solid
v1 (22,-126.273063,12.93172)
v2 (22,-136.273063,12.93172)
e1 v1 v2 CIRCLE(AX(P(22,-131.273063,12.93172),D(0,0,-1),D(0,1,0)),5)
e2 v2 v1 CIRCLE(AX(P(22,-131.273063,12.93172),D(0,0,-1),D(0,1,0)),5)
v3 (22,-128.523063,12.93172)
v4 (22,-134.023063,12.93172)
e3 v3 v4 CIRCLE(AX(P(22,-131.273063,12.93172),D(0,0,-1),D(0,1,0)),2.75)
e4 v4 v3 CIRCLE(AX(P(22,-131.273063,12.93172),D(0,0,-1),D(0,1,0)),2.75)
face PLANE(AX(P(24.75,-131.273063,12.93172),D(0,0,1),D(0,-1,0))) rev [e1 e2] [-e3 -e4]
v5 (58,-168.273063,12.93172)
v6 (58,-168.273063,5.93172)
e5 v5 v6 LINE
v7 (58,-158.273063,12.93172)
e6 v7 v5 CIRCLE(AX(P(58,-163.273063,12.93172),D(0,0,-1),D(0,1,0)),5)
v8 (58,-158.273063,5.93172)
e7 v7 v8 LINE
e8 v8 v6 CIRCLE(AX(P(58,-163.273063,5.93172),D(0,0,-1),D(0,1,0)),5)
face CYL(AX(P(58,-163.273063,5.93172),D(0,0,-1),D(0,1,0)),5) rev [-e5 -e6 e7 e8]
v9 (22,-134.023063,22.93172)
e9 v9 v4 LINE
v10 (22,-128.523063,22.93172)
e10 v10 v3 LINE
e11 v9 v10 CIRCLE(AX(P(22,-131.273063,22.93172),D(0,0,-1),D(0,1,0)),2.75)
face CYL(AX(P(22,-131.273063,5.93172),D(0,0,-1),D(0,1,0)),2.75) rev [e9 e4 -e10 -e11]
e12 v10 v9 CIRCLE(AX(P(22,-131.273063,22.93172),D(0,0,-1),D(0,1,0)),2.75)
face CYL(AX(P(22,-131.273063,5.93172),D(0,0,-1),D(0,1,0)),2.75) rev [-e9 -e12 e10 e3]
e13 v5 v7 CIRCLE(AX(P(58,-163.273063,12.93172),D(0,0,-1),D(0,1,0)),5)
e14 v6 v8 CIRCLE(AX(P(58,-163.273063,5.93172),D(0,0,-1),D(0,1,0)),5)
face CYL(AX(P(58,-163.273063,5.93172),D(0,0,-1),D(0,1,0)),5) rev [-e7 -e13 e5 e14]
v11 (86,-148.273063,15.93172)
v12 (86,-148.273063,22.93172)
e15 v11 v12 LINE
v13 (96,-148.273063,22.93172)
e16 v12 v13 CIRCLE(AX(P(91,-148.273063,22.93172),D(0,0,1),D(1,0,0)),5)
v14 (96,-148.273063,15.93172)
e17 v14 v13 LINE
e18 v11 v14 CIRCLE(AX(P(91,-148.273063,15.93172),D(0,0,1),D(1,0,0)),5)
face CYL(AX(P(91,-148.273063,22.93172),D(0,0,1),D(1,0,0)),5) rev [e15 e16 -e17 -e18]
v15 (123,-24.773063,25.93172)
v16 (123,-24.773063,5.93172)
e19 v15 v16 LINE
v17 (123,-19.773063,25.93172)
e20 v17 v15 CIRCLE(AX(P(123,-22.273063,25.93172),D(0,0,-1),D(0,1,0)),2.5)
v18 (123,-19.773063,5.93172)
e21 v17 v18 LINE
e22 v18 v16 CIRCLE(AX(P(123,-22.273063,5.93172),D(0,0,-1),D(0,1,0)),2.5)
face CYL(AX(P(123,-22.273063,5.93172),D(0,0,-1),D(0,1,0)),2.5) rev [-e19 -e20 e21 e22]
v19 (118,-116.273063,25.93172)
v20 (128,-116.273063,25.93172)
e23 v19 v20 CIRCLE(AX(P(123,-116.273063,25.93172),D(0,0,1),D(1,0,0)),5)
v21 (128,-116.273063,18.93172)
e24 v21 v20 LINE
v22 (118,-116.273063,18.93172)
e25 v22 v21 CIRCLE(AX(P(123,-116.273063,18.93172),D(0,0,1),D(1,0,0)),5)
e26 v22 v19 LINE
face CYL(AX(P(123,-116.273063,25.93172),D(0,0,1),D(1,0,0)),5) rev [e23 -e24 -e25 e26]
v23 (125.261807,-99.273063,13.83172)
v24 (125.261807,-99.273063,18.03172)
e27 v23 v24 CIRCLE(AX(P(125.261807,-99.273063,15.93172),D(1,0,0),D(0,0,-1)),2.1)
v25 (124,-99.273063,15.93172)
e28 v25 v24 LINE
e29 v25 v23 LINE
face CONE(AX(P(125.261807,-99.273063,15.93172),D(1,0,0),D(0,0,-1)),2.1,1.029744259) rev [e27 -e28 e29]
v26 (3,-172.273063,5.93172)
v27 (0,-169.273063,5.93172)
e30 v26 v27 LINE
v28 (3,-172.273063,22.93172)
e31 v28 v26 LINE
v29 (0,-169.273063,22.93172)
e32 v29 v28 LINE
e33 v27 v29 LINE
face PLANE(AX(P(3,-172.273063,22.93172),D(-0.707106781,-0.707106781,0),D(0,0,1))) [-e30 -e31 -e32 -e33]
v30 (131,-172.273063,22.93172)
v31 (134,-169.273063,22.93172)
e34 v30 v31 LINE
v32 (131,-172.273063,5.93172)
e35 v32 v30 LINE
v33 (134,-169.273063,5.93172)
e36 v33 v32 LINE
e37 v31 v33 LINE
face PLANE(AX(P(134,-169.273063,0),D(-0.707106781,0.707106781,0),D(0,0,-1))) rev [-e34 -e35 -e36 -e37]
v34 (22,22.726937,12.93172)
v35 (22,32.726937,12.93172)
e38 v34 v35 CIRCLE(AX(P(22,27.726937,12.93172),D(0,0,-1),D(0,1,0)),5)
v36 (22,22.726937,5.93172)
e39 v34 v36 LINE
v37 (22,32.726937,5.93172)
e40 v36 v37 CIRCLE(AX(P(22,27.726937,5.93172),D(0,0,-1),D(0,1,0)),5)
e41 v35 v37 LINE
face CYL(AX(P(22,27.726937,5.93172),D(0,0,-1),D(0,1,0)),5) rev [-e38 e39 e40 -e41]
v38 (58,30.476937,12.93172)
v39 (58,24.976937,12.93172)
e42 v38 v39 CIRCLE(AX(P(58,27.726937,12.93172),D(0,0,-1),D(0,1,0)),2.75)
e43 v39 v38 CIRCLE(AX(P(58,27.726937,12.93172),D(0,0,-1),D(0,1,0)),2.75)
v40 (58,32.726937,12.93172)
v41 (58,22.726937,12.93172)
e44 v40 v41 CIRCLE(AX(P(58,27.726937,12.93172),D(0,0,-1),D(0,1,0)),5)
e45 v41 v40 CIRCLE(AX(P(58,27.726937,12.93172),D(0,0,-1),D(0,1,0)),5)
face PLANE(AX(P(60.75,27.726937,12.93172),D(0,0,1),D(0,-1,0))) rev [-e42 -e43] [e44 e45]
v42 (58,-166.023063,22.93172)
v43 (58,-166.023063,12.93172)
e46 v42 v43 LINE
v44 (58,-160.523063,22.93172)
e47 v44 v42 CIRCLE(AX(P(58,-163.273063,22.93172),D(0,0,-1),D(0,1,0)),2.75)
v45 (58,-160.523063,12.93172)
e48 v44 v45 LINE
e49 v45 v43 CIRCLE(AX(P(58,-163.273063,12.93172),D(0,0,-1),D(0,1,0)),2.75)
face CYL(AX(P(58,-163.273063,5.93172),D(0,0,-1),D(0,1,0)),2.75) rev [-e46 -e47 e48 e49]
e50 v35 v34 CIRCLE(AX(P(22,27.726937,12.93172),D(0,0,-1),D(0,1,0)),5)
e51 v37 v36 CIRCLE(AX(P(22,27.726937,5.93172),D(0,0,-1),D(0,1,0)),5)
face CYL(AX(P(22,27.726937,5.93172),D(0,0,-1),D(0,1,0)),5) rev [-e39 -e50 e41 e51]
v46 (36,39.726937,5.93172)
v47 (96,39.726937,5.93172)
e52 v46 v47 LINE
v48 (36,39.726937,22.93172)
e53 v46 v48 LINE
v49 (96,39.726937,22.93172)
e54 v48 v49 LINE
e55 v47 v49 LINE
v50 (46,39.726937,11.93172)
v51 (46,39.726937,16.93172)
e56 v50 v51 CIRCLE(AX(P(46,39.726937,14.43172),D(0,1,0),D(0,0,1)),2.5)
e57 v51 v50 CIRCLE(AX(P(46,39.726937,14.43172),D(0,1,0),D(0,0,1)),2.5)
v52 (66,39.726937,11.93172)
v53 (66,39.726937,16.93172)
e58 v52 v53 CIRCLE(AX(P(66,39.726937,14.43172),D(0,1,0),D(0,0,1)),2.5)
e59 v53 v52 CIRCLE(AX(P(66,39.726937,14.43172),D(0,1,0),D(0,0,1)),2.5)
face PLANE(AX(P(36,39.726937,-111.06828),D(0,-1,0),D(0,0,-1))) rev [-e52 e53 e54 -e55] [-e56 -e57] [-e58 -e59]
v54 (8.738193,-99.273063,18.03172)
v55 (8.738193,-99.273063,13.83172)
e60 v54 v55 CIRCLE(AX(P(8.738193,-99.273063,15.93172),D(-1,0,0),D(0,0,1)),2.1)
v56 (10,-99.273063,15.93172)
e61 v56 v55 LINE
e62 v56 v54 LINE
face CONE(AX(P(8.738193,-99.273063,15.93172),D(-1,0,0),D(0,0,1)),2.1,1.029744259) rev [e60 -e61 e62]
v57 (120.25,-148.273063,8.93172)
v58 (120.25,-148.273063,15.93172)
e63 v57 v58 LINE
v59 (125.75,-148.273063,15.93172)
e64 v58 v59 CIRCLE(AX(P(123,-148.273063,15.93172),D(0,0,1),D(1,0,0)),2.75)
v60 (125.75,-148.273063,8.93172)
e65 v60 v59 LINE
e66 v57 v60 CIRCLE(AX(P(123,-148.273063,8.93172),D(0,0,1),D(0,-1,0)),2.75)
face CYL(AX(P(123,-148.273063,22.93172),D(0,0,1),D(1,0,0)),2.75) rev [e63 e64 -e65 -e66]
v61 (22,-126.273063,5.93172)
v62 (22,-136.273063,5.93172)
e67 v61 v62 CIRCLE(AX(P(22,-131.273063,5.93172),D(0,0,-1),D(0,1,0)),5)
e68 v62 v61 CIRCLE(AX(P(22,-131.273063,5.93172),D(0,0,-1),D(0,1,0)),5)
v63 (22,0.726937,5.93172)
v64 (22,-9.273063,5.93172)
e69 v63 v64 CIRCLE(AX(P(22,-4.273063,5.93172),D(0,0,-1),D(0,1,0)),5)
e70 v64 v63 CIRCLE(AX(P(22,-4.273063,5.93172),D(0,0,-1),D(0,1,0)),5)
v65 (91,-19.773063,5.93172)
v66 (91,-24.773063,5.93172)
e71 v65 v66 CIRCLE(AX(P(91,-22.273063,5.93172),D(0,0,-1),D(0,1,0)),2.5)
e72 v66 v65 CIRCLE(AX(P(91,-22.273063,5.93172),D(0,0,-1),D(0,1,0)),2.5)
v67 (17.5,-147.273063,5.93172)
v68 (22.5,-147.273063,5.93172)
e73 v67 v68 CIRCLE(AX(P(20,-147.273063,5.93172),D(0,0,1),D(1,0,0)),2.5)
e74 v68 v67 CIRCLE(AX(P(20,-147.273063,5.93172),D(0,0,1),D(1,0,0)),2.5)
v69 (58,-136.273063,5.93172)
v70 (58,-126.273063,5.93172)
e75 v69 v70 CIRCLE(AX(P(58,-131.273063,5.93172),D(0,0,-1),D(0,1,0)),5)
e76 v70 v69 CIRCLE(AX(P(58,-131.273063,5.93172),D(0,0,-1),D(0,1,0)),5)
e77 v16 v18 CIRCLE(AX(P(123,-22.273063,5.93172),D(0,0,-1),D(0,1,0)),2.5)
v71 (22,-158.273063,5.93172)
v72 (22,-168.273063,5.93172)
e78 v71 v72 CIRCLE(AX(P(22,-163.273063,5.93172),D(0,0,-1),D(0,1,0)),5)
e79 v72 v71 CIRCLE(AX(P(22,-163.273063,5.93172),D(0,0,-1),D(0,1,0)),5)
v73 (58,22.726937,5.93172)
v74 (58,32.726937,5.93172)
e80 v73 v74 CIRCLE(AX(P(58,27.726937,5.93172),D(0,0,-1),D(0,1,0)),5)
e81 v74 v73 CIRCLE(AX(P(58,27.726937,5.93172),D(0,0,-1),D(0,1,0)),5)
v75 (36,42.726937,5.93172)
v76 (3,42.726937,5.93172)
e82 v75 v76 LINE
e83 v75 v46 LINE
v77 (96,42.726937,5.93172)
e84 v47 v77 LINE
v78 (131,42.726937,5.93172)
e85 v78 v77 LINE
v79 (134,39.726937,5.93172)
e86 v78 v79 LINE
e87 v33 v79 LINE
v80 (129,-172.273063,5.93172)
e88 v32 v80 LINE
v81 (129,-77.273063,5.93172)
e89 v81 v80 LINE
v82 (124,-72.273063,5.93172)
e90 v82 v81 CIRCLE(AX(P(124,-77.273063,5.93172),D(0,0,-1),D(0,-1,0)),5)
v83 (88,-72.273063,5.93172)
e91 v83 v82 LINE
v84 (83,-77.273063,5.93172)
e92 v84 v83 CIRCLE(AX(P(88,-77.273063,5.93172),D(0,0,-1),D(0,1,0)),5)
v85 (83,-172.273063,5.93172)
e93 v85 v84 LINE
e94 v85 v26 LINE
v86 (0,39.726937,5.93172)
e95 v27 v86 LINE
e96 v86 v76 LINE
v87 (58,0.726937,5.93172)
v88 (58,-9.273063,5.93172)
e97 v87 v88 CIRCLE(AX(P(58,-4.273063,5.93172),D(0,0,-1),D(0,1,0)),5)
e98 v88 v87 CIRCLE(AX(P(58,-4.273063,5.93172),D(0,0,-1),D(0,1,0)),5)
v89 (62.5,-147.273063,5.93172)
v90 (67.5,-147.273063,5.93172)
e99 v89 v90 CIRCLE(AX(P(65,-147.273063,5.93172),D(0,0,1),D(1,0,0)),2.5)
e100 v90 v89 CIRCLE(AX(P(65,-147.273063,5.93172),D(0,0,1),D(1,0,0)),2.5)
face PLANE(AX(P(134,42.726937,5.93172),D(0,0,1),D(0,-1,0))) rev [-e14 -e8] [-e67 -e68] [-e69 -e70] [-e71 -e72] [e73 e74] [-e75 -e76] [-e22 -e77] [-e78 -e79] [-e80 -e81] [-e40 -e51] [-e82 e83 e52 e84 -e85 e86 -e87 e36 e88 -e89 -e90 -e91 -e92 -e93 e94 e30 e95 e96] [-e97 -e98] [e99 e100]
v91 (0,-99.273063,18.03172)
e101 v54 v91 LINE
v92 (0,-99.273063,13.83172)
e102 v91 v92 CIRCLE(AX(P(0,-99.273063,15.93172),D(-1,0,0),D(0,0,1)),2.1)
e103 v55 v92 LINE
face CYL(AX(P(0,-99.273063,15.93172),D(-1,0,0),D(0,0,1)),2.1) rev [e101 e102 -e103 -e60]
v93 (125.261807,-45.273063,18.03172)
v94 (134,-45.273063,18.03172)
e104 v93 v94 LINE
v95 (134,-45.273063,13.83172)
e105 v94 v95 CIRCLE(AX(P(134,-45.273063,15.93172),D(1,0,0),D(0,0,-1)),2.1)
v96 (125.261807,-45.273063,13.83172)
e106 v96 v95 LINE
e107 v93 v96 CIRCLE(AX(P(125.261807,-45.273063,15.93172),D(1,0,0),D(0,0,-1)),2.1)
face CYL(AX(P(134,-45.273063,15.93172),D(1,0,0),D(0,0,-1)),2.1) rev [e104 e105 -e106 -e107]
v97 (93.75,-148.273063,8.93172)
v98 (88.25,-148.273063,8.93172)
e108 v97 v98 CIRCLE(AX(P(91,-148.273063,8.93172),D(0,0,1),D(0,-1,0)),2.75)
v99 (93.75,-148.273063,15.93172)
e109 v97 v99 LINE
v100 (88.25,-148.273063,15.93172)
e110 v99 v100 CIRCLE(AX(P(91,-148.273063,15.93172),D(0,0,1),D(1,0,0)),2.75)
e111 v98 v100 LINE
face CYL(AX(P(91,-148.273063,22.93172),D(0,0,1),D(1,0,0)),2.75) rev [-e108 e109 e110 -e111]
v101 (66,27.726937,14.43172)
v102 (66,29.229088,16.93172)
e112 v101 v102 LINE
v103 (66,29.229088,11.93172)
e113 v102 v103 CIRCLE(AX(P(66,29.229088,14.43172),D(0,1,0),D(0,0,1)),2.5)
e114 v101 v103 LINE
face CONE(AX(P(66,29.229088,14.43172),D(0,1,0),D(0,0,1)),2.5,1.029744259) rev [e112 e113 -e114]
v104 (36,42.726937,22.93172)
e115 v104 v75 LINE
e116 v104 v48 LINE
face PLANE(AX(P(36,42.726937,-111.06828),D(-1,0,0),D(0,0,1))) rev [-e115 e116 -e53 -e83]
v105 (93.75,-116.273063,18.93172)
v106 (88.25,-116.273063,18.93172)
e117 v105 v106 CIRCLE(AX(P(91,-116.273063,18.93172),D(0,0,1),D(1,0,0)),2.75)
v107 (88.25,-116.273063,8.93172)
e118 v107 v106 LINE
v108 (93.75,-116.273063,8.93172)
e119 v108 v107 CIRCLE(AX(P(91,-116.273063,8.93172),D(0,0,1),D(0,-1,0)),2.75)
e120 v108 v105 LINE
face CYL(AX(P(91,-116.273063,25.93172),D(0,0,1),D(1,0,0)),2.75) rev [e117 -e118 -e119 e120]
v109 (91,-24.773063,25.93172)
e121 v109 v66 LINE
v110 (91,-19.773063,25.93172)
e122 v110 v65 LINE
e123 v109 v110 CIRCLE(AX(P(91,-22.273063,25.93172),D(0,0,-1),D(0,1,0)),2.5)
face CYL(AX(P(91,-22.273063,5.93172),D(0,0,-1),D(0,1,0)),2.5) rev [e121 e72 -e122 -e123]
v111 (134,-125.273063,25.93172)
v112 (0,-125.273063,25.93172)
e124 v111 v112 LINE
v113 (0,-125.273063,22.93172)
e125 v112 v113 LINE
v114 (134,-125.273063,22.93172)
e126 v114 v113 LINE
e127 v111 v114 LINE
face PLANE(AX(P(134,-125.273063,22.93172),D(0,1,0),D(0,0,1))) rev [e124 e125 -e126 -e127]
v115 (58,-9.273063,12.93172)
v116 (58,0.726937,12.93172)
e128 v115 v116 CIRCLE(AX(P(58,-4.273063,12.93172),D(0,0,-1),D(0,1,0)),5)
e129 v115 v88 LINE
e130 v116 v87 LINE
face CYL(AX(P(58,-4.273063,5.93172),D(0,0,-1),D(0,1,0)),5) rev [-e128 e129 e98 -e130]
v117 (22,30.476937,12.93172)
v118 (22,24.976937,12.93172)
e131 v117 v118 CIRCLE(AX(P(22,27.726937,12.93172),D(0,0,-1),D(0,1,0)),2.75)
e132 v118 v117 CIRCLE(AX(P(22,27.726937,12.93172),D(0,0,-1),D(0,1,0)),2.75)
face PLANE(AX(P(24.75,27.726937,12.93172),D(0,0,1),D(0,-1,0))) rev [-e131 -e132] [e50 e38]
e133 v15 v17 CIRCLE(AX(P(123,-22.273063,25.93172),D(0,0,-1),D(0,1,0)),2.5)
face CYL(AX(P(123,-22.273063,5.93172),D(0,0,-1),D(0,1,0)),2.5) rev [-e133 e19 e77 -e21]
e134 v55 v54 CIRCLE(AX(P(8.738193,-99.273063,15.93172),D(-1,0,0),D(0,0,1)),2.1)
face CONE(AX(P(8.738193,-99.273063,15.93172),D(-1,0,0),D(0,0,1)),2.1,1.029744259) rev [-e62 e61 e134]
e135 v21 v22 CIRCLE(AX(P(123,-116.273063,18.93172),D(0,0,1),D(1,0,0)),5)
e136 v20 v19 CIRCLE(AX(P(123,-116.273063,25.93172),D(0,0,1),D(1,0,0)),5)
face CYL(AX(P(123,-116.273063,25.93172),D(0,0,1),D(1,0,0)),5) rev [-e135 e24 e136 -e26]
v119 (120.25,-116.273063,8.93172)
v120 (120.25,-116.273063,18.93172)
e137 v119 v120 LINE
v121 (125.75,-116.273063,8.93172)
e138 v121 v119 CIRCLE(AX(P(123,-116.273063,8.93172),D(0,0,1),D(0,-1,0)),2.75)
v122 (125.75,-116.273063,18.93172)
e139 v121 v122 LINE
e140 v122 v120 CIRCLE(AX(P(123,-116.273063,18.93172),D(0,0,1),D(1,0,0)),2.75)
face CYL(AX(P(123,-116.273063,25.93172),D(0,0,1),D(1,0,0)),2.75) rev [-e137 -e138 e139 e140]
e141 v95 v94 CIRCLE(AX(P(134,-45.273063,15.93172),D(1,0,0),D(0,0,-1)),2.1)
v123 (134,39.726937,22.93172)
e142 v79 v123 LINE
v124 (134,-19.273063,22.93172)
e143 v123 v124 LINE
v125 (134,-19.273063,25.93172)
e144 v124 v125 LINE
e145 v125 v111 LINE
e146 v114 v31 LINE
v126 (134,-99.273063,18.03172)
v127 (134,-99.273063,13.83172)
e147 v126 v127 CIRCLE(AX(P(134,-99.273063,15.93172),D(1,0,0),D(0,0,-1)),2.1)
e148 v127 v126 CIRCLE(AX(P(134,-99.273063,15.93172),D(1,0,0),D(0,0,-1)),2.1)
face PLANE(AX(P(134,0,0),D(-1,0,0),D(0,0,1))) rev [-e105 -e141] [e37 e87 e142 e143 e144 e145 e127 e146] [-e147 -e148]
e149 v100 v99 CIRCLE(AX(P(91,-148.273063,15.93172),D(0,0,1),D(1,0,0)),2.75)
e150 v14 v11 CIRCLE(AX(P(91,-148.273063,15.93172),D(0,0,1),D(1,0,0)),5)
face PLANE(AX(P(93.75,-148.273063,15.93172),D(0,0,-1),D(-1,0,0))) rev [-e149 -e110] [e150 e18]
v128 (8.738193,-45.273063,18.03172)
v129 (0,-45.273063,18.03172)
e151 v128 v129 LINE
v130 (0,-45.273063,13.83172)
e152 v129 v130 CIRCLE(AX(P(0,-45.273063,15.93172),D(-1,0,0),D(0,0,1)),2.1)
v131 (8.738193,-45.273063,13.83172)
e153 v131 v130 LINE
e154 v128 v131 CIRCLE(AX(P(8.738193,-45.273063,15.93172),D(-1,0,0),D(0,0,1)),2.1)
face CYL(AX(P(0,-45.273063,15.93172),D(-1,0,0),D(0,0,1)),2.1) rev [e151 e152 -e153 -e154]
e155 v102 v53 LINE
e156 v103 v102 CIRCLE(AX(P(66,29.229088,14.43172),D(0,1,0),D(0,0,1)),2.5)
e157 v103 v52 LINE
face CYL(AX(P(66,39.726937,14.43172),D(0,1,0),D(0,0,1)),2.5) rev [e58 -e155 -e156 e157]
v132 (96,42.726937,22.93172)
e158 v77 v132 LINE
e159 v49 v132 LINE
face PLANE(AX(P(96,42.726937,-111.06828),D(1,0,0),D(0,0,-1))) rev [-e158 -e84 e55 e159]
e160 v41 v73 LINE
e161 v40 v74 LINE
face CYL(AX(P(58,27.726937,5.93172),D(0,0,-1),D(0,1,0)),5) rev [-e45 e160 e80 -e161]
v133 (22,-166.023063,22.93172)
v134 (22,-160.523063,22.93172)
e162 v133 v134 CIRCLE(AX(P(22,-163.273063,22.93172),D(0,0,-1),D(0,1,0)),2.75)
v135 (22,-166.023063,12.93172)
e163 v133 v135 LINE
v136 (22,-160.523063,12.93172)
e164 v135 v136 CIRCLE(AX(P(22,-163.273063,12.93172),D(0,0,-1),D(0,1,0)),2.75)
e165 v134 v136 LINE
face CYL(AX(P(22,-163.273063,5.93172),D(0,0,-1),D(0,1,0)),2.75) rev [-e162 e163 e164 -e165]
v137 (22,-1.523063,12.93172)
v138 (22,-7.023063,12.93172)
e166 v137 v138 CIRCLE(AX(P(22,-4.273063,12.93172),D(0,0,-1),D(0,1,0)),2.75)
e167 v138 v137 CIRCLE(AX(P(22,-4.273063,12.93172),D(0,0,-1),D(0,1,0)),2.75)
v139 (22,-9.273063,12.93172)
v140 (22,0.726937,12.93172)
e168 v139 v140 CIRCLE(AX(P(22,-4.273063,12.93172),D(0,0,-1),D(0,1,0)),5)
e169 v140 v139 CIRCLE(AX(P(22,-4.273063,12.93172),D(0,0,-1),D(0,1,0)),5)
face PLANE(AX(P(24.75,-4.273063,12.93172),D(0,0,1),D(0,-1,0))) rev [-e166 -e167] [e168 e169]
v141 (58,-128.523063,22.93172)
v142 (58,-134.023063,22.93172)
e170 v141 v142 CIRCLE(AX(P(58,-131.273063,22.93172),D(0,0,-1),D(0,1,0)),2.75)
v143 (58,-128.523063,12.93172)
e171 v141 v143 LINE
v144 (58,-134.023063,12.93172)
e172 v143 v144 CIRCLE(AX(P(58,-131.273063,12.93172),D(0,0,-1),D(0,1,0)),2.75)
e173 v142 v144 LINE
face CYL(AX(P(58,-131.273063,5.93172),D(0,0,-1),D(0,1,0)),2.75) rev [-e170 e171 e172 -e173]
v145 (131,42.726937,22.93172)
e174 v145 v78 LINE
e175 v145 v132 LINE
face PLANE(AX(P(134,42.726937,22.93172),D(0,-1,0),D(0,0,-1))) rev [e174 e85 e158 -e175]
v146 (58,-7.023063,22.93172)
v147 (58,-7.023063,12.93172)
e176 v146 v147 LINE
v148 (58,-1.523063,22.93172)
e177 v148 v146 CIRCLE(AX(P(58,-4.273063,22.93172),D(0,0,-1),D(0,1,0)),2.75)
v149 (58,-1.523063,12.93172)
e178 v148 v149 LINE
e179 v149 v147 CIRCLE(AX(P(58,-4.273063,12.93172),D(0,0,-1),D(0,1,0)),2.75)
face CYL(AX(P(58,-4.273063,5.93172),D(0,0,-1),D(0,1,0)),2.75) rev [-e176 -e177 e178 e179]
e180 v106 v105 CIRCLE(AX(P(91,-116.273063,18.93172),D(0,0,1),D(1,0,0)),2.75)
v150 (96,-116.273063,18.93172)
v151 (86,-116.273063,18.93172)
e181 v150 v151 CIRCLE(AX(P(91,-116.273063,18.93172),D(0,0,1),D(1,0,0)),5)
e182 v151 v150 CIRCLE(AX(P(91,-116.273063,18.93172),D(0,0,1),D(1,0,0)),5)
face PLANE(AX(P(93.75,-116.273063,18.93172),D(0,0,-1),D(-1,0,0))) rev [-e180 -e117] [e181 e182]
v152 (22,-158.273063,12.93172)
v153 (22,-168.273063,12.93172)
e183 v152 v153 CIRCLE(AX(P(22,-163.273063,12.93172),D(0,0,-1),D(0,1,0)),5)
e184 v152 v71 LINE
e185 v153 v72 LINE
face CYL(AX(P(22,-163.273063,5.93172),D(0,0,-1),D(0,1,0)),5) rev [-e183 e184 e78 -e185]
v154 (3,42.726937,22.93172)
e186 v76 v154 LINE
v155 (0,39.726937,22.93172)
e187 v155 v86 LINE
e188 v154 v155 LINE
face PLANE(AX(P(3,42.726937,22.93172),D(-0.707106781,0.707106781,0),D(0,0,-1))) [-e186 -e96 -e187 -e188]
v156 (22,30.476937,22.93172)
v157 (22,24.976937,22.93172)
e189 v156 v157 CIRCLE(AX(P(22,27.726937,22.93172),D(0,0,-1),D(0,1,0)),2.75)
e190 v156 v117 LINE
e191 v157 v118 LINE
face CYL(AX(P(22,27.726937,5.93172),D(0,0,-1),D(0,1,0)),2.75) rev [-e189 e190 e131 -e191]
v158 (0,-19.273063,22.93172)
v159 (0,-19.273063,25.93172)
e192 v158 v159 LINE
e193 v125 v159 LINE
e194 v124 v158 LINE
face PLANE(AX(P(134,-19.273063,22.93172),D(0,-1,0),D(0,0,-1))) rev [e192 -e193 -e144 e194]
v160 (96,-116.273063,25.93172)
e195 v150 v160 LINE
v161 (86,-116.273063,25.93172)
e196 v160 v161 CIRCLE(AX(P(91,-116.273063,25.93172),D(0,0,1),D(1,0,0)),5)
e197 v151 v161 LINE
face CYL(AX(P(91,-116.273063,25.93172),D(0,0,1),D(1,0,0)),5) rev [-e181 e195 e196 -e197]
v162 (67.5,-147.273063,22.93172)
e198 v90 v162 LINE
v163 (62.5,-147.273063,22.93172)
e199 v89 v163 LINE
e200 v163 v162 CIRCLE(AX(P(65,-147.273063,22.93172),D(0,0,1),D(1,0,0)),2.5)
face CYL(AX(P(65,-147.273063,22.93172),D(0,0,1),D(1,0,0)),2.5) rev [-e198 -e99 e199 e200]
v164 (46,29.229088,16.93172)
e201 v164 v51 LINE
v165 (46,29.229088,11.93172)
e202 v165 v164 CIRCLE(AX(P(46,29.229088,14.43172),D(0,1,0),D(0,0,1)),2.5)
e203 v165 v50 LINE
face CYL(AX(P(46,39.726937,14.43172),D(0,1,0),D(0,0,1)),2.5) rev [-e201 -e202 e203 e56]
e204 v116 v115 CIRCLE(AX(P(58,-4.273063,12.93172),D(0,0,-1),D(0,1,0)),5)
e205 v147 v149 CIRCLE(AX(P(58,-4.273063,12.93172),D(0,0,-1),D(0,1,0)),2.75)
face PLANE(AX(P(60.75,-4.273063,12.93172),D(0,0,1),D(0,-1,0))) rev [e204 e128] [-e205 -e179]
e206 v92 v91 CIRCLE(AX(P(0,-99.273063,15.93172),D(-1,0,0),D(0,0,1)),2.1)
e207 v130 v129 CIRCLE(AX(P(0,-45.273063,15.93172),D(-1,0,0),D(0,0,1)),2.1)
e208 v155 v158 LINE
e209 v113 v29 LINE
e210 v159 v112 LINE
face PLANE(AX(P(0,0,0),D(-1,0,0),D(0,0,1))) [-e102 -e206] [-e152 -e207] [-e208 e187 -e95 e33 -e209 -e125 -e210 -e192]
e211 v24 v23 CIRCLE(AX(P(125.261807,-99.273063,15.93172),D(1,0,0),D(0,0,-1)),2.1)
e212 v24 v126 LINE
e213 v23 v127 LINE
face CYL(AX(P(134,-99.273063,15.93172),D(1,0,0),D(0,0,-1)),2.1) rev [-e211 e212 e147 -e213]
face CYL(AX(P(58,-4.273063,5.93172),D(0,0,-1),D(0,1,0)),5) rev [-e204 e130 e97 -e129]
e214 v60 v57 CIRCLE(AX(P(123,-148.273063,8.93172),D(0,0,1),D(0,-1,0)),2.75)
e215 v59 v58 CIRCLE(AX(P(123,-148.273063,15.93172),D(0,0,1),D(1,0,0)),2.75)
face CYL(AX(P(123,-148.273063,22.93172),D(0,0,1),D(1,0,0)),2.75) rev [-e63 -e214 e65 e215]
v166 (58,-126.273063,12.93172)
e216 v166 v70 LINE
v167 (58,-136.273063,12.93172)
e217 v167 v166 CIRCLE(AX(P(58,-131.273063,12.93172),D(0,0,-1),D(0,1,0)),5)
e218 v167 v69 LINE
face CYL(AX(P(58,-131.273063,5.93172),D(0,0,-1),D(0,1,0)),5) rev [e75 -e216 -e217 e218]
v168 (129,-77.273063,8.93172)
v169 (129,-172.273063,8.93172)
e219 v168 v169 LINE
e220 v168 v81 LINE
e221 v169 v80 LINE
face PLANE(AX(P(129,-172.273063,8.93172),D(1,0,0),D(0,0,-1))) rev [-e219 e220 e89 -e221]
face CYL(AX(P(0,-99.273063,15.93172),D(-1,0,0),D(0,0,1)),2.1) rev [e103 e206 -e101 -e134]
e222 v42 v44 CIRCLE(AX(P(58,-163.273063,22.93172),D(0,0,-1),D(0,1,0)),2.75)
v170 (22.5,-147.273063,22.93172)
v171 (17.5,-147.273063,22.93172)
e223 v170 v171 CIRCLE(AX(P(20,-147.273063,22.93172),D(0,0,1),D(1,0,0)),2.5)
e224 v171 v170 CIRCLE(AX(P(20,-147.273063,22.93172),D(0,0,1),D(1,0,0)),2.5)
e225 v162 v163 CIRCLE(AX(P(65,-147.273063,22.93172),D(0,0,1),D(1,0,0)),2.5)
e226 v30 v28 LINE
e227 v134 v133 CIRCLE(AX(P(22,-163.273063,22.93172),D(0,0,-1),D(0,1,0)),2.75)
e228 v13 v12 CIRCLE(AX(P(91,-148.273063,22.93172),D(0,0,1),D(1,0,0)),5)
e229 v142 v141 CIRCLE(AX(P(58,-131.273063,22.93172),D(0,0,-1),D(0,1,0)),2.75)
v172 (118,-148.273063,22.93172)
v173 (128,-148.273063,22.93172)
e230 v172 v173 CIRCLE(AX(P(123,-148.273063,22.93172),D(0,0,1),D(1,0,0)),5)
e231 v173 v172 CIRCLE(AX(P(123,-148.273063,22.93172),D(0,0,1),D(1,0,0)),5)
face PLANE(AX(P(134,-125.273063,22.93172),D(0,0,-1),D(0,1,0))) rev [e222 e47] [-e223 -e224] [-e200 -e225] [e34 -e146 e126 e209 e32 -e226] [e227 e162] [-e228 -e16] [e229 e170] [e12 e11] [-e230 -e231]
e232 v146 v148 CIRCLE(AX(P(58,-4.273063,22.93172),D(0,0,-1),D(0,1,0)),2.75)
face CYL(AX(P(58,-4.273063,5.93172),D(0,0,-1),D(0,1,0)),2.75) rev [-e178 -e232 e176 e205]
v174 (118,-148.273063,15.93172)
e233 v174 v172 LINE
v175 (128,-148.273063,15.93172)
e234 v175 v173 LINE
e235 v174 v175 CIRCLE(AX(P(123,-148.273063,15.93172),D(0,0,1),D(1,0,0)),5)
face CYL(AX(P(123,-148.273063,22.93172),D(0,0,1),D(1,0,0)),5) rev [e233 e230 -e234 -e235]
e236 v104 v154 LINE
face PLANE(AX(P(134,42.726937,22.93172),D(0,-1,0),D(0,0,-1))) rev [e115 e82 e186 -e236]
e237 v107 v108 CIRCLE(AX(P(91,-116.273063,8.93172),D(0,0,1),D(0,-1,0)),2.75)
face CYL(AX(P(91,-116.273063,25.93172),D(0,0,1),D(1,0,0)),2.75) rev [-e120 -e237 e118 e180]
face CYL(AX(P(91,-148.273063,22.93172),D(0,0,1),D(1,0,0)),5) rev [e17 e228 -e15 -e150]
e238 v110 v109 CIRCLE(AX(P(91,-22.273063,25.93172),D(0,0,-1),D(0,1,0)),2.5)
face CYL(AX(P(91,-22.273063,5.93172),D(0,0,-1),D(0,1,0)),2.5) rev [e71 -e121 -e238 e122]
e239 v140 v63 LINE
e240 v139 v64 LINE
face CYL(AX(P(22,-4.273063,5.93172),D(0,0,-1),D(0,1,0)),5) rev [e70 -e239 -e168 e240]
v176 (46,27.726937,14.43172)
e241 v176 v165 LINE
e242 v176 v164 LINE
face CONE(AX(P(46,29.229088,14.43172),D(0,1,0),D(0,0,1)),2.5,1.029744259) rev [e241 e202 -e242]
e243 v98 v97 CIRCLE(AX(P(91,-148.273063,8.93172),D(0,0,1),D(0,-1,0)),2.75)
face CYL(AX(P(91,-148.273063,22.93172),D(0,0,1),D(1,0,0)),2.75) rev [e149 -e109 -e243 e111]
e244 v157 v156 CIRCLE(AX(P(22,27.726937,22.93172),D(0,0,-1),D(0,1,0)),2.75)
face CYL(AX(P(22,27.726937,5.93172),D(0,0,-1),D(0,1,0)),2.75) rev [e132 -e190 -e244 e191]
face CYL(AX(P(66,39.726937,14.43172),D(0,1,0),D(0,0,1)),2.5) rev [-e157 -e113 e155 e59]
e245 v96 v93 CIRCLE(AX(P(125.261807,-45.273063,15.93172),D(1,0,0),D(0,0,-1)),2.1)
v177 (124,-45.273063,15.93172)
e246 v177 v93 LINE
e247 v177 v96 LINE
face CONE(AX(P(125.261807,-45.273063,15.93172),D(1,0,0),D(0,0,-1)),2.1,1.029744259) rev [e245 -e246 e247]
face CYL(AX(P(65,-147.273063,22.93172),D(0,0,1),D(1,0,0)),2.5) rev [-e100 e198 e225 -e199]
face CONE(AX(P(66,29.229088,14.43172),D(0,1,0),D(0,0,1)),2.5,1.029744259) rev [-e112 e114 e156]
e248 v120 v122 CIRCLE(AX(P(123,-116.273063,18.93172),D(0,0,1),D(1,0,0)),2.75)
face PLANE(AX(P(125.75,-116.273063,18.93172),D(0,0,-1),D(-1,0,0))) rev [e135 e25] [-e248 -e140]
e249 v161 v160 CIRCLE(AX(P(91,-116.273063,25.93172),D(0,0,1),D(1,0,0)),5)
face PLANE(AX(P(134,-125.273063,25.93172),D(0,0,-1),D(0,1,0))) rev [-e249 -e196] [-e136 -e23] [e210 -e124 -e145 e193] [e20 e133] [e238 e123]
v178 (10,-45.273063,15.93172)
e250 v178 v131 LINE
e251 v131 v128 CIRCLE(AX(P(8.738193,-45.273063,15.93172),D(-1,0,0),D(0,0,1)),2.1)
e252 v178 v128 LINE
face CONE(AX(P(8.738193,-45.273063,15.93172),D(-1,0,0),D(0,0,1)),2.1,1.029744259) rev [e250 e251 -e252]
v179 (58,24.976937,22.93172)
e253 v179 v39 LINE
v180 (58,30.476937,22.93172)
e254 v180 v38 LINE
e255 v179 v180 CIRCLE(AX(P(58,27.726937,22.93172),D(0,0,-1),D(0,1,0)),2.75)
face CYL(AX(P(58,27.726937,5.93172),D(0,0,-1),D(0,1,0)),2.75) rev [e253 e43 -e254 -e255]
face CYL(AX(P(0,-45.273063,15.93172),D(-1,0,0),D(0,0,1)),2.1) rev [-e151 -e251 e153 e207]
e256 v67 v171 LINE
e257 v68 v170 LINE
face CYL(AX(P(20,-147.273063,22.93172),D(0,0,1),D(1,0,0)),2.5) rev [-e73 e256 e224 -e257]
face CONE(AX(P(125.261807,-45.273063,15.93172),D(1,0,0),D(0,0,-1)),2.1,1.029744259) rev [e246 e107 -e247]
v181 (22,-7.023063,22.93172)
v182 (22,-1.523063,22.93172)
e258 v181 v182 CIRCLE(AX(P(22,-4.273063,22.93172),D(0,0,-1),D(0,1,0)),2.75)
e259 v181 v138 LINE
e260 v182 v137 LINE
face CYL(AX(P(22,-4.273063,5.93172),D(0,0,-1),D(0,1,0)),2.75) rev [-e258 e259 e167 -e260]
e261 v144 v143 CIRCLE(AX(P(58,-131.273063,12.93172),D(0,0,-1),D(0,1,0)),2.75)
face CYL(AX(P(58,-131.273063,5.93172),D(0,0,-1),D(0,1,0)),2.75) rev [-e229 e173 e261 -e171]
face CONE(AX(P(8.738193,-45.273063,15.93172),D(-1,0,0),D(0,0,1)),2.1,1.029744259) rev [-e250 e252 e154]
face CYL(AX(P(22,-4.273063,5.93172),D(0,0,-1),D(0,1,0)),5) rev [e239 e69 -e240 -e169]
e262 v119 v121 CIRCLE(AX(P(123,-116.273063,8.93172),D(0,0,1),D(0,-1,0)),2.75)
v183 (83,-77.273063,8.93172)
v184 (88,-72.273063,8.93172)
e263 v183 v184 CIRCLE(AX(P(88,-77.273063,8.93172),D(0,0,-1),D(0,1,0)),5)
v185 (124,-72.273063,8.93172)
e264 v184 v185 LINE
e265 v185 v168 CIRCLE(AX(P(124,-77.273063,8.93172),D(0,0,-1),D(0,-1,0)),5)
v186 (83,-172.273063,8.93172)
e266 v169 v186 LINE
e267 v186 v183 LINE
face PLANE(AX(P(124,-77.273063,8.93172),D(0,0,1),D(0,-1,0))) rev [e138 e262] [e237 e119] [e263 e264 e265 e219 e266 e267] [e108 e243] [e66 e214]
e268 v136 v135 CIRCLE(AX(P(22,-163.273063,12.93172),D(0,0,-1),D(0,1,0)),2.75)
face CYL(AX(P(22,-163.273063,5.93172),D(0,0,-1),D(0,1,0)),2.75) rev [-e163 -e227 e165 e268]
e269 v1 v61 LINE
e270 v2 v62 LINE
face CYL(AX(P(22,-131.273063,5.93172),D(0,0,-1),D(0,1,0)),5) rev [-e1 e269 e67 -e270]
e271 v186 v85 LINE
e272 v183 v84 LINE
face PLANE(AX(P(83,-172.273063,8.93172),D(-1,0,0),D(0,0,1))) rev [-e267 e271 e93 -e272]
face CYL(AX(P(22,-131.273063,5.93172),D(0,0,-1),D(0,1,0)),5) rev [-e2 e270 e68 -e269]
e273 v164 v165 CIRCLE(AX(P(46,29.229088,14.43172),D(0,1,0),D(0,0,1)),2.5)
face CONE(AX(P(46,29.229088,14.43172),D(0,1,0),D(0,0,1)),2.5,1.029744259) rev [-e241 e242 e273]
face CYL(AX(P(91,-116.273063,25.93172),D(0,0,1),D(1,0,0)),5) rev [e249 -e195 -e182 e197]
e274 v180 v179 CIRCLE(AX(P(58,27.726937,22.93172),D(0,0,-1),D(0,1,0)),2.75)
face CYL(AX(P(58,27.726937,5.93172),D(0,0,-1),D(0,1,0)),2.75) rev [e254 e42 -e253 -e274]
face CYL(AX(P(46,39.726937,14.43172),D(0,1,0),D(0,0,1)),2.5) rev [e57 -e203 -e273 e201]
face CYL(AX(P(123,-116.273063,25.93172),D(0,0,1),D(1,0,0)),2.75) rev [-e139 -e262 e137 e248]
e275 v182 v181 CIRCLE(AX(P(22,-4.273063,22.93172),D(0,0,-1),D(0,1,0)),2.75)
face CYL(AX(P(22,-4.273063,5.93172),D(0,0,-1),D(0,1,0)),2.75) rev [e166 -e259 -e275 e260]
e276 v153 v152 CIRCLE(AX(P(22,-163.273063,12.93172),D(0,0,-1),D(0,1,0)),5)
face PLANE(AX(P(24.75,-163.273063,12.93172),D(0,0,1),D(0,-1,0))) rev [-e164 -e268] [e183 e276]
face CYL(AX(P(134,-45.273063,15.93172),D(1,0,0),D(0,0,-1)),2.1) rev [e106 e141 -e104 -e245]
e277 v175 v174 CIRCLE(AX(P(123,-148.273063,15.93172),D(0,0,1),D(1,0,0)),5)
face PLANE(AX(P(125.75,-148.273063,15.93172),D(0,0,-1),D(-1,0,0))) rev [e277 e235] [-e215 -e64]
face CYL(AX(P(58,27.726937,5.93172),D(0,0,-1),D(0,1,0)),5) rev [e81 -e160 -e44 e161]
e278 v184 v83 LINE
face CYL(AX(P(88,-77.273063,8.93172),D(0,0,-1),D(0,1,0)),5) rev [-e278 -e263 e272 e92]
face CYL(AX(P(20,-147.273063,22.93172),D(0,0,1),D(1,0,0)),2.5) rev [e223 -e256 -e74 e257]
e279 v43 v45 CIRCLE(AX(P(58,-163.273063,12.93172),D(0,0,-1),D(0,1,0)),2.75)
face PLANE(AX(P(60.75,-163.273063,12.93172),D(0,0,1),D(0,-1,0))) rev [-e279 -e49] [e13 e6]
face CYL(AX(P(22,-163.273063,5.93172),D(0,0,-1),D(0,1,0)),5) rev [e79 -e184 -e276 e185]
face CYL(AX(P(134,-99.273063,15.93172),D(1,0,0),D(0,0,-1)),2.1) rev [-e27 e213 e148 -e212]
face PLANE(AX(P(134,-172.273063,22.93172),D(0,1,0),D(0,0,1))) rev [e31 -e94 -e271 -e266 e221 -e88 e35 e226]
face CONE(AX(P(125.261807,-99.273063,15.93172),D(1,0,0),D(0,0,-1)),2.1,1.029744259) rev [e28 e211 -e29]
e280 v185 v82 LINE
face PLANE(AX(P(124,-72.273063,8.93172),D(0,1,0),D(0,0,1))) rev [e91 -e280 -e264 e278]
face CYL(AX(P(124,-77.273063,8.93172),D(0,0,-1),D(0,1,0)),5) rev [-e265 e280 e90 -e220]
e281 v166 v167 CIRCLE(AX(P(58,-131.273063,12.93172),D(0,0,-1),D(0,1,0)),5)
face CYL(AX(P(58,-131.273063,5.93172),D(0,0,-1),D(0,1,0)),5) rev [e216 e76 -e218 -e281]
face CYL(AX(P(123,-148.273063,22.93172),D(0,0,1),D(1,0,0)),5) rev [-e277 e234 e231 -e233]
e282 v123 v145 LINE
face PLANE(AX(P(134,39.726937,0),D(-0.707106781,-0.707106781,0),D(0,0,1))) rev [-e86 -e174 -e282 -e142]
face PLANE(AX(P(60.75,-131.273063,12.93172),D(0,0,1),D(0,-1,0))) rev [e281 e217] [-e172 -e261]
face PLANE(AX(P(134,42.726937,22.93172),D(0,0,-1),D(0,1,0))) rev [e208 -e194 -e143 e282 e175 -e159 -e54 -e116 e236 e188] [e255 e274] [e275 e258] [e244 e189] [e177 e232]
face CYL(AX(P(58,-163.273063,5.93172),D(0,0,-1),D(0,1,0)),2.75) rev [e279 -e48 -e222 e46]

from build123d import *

# Parameters (mm, degrees)
BOSS_EXTRUDE1_DEPTH   = 134
SKETCH2_W             = 60
SKETCH2_H             = 3
CUT_EXTRUDE1_DEPTH    = 134
CHAMFER1_SIZE         = 3
M5_TAPPED_HOLE1_D     = 4.2
M5_TAPPED_HOLE1_DEPTH = 8.7381927
M5_TAPPED_HOLE1_TIP   = 1.2618073
M5_TAPPED_HOLE2_D     = 4.2
M5_TAPPED_HOLE2_DEPTH = 8.7381927
M5_TAPPED_HOLE2_TIP   = 1.2618073
M6_TAPPED_HOLE1_D     = 5
M6_TAPPED_HOLE1_DEPTH = 10.497848452
M6_TAPPED_HOLE1_TIP   = 1.502151548
M6_TAPPED_HOLE2_D     = 5
HOLE1_D               = 5.5
HOLE1_CBORE_D         = 10
HOLE1_CBORE_DEPTH     = 7
CUT_EXTRUDE2_DEPTH    = 3
HOLE2_D               = 5.5
HOLE2_CBORE_D         = 10
HOLE2_CBORE_DEPTH     = 7
HOLE3_D               = 5.5
HOLE3_CBORE_D         = 10
HOLE3_CBORE_DEPTH     = 7
M6_TAPPED_HOLE3_D     = 5


with BuildPart() as part:
    # Sketch1 → Boss-Extrude1 (new body)
    with BuildSketch(Plane(origin=(0, 3.607618474, 0), x_dir=(0, 0, -1), z_dir=(1, 0, 0))):
        Polygon((-22.931720467, -128.880681818), (-22.931720467, -175.880681818), (-5.931720467, -175.880681818), (-5.931720467, 39.119318182), (-22.931720467, 39.119318182), (-22.931720467, -22.880681818), (-25.931720467, -22.880681818), (-25.931720467, -128.880681818), align=None)
    extrude(amount=BOSS_EXTRUDE1_DEPTH)

    # Sketch2 → Cut-Extrude1 (cut)
    with BuildSketch(Plane(origin=(0, 3.607618474, 22.931720467), x_dir=(1, 0, 0), z_dir=(0, 0, 1))):
        with Locations((66, 37.619318182)):
            Rectangle(SKETCH2_W, SKETCH2_H)
    extrude(amount=-CUT_EXTRUDE1_DEPTH, mode=Mode.SUBTRACT)

    # Chamfer1
    chamfer1_edges = [part.edges().sort_by_distance(p)[0] for p in [
        (134, -172.273063344, 14.431720467),
        (134, 42.726936656, 14.431720467),
        (0, 42.726936656, 14.431720467),
        (0, -172.273063344, 14.431720467),
    ]]
    chamfer(chamfer1_edges, length=CHAMFER1_SIZE)

    # M5 Tapped Hole1
    with Locations(Plane(origin=(134, 0, 0), x_dir=(0, 0, -1), z_dir=(1, 0, 0))):
        with Locations((-15.931720467, -45.273063344), (-15.931720467, -99.273063344)):
            Hole(M5_TAPPED_HOLE1_D / 2, depth=M5_TAPPED_HOLE1_DEPTH)
            with Locations((0, 0, -(M5_TAPPED_HOLE1_DEPTH + M5_TAPPED_HOLE1_TIP / 2))):  # 118° drill point
                Cone(0, M5_TAPPED_HOLE1_D / 2, M5_TAPPED_HOLE1_TIP, mode=Mode.SUBTRACT)

    # M5 Tapped Hole2
    with Locations(Plane.ZY):
        with Locations((15.931720467, -45.273063344), (15.931720467, -99.273063344)):
            Hole(M5_TAPPED_HOLE2_D / 2, depth=M5_TAPPED_HOLE2_DEPTH)
            with Locations((0, 0, -(M5_TAPPED_HOLE2_DEPTH + M5_TAPPED_HOLE2_TIP / 2))):  # 118° drill point
                Cone(0, M5_TAPPED_HOLE2_D / 2, M5_TAPPED_HOLE2_TIP, mode=Mode.SUBTRACT)

    # M6 Tapped Hole1
    with Locations(Plane(origin=(0, 39.726936656, 0), x_dir=(1, 0, 0), z_dir=(0, 1, 0))):
        with Locations((66, -14.431720467), (46, -14.431720467)):
            Hole(M6_TAPPED_HOLE1_D / 2, depth=M6_TAPPED_HOLE1_DEPTH)
            with Locations((0, 0, -(M6_TAPPED_HOLE1_DEPTH + M6_TAPPED_HOLE1_TIP / 2))):  # 118° drill point
                Cone(0, M6_TAPPED_HOLE1_D / 2, M6_TAPPED_HOLE1_TIP, mode=Mode.SUBTRACT)

    # M6 Tapped Hole2 (through all)
    with Locations(Plane(origin=(0, 0, 5.931720467), x_dir=(-1, 0, 0), z_dir=(0, 0, -1))):
        with Locations((-123, -22.273063344), (-91, -22.273063344)):
            Hole(M6_TAPPED_HOLE2_D / 2)

    # Hole1 (through all)
    with Locations(Plane(origin=(0, 0, 5.931720467), x_dir=(-1, 0, 0), z_dir=(0, 0, -1))):
        with Locations((-58, 27.726936656), (-22, 27.726936656), (-22, -4.273063344), (-58, -4.273063344), (-58, -131.273063344), (-58, -163.273063344), (-22, -163.273063344), (-22, -131.273063344)):
            CounterBoreHole(HOLE1_D / 2, HOLE1_CBORE_D / 2, HOLE1_CBORE_DEPTH)

    # Sketch17 → Cut-Extrude2 (cut)
    with BuildSketch(Plane(origin=(0, 0, 5.931720467), x_dir=(-1, 0, 0), z_dir=(0, 0, -1))):
        with BuildLine():
            Line((-129, -172.273063344), (-83, -172.273063344))
            Line((-83, -172.273063344), (-83, -77.273063344))
            ThreePointArc((-83, -77.273063344), (-84.464466094, -73.737529438), (-88, -72.273063344))
            Line((-88, -72.273063344), (-124, -72.273063344))
            ThreePointArc((-124, -72.273063344), (-127.535533906, -73.737529438), (-129, -77.273063344))
            Line((-129, -77.273063344), (-129, -172.273063344))
        make_face()
    extrude(amount=-CUT_EXTRUDE2_DEPTH, mode=Mode.SUBTRACT)

    # Hole2 (through all)
    with Locations(Plane.XY.offset(25.931720467)):
        with Locations((91, -116.273063344), (123, -116.273063344)):
            CounterBoreHole(HOLE2_D / 2, HOLE2_CBORE_D / 2, HOLE2_CBORE_DEPTH)

    # Hole3 (through all)
    with Locations(Plane.XY.offset(22.931720467)):
        with Locations((91, -148.273063344), (123, -148.273063344)):
            CounterBoreHole(HOLE3_D / 2, HOLE3_CBORE_D / 2, HOLE3_CBORE_DEPTH)

    # M6 Tapped Hole3 (through all)
    with Locations(Plane.XY.offset(22.931720467)):
        with Locations((20, -147.273063344), (65, -147.273063344)):
            Hole(M6_TAPPED_HOLE3_D / 2)


solid = part.part
